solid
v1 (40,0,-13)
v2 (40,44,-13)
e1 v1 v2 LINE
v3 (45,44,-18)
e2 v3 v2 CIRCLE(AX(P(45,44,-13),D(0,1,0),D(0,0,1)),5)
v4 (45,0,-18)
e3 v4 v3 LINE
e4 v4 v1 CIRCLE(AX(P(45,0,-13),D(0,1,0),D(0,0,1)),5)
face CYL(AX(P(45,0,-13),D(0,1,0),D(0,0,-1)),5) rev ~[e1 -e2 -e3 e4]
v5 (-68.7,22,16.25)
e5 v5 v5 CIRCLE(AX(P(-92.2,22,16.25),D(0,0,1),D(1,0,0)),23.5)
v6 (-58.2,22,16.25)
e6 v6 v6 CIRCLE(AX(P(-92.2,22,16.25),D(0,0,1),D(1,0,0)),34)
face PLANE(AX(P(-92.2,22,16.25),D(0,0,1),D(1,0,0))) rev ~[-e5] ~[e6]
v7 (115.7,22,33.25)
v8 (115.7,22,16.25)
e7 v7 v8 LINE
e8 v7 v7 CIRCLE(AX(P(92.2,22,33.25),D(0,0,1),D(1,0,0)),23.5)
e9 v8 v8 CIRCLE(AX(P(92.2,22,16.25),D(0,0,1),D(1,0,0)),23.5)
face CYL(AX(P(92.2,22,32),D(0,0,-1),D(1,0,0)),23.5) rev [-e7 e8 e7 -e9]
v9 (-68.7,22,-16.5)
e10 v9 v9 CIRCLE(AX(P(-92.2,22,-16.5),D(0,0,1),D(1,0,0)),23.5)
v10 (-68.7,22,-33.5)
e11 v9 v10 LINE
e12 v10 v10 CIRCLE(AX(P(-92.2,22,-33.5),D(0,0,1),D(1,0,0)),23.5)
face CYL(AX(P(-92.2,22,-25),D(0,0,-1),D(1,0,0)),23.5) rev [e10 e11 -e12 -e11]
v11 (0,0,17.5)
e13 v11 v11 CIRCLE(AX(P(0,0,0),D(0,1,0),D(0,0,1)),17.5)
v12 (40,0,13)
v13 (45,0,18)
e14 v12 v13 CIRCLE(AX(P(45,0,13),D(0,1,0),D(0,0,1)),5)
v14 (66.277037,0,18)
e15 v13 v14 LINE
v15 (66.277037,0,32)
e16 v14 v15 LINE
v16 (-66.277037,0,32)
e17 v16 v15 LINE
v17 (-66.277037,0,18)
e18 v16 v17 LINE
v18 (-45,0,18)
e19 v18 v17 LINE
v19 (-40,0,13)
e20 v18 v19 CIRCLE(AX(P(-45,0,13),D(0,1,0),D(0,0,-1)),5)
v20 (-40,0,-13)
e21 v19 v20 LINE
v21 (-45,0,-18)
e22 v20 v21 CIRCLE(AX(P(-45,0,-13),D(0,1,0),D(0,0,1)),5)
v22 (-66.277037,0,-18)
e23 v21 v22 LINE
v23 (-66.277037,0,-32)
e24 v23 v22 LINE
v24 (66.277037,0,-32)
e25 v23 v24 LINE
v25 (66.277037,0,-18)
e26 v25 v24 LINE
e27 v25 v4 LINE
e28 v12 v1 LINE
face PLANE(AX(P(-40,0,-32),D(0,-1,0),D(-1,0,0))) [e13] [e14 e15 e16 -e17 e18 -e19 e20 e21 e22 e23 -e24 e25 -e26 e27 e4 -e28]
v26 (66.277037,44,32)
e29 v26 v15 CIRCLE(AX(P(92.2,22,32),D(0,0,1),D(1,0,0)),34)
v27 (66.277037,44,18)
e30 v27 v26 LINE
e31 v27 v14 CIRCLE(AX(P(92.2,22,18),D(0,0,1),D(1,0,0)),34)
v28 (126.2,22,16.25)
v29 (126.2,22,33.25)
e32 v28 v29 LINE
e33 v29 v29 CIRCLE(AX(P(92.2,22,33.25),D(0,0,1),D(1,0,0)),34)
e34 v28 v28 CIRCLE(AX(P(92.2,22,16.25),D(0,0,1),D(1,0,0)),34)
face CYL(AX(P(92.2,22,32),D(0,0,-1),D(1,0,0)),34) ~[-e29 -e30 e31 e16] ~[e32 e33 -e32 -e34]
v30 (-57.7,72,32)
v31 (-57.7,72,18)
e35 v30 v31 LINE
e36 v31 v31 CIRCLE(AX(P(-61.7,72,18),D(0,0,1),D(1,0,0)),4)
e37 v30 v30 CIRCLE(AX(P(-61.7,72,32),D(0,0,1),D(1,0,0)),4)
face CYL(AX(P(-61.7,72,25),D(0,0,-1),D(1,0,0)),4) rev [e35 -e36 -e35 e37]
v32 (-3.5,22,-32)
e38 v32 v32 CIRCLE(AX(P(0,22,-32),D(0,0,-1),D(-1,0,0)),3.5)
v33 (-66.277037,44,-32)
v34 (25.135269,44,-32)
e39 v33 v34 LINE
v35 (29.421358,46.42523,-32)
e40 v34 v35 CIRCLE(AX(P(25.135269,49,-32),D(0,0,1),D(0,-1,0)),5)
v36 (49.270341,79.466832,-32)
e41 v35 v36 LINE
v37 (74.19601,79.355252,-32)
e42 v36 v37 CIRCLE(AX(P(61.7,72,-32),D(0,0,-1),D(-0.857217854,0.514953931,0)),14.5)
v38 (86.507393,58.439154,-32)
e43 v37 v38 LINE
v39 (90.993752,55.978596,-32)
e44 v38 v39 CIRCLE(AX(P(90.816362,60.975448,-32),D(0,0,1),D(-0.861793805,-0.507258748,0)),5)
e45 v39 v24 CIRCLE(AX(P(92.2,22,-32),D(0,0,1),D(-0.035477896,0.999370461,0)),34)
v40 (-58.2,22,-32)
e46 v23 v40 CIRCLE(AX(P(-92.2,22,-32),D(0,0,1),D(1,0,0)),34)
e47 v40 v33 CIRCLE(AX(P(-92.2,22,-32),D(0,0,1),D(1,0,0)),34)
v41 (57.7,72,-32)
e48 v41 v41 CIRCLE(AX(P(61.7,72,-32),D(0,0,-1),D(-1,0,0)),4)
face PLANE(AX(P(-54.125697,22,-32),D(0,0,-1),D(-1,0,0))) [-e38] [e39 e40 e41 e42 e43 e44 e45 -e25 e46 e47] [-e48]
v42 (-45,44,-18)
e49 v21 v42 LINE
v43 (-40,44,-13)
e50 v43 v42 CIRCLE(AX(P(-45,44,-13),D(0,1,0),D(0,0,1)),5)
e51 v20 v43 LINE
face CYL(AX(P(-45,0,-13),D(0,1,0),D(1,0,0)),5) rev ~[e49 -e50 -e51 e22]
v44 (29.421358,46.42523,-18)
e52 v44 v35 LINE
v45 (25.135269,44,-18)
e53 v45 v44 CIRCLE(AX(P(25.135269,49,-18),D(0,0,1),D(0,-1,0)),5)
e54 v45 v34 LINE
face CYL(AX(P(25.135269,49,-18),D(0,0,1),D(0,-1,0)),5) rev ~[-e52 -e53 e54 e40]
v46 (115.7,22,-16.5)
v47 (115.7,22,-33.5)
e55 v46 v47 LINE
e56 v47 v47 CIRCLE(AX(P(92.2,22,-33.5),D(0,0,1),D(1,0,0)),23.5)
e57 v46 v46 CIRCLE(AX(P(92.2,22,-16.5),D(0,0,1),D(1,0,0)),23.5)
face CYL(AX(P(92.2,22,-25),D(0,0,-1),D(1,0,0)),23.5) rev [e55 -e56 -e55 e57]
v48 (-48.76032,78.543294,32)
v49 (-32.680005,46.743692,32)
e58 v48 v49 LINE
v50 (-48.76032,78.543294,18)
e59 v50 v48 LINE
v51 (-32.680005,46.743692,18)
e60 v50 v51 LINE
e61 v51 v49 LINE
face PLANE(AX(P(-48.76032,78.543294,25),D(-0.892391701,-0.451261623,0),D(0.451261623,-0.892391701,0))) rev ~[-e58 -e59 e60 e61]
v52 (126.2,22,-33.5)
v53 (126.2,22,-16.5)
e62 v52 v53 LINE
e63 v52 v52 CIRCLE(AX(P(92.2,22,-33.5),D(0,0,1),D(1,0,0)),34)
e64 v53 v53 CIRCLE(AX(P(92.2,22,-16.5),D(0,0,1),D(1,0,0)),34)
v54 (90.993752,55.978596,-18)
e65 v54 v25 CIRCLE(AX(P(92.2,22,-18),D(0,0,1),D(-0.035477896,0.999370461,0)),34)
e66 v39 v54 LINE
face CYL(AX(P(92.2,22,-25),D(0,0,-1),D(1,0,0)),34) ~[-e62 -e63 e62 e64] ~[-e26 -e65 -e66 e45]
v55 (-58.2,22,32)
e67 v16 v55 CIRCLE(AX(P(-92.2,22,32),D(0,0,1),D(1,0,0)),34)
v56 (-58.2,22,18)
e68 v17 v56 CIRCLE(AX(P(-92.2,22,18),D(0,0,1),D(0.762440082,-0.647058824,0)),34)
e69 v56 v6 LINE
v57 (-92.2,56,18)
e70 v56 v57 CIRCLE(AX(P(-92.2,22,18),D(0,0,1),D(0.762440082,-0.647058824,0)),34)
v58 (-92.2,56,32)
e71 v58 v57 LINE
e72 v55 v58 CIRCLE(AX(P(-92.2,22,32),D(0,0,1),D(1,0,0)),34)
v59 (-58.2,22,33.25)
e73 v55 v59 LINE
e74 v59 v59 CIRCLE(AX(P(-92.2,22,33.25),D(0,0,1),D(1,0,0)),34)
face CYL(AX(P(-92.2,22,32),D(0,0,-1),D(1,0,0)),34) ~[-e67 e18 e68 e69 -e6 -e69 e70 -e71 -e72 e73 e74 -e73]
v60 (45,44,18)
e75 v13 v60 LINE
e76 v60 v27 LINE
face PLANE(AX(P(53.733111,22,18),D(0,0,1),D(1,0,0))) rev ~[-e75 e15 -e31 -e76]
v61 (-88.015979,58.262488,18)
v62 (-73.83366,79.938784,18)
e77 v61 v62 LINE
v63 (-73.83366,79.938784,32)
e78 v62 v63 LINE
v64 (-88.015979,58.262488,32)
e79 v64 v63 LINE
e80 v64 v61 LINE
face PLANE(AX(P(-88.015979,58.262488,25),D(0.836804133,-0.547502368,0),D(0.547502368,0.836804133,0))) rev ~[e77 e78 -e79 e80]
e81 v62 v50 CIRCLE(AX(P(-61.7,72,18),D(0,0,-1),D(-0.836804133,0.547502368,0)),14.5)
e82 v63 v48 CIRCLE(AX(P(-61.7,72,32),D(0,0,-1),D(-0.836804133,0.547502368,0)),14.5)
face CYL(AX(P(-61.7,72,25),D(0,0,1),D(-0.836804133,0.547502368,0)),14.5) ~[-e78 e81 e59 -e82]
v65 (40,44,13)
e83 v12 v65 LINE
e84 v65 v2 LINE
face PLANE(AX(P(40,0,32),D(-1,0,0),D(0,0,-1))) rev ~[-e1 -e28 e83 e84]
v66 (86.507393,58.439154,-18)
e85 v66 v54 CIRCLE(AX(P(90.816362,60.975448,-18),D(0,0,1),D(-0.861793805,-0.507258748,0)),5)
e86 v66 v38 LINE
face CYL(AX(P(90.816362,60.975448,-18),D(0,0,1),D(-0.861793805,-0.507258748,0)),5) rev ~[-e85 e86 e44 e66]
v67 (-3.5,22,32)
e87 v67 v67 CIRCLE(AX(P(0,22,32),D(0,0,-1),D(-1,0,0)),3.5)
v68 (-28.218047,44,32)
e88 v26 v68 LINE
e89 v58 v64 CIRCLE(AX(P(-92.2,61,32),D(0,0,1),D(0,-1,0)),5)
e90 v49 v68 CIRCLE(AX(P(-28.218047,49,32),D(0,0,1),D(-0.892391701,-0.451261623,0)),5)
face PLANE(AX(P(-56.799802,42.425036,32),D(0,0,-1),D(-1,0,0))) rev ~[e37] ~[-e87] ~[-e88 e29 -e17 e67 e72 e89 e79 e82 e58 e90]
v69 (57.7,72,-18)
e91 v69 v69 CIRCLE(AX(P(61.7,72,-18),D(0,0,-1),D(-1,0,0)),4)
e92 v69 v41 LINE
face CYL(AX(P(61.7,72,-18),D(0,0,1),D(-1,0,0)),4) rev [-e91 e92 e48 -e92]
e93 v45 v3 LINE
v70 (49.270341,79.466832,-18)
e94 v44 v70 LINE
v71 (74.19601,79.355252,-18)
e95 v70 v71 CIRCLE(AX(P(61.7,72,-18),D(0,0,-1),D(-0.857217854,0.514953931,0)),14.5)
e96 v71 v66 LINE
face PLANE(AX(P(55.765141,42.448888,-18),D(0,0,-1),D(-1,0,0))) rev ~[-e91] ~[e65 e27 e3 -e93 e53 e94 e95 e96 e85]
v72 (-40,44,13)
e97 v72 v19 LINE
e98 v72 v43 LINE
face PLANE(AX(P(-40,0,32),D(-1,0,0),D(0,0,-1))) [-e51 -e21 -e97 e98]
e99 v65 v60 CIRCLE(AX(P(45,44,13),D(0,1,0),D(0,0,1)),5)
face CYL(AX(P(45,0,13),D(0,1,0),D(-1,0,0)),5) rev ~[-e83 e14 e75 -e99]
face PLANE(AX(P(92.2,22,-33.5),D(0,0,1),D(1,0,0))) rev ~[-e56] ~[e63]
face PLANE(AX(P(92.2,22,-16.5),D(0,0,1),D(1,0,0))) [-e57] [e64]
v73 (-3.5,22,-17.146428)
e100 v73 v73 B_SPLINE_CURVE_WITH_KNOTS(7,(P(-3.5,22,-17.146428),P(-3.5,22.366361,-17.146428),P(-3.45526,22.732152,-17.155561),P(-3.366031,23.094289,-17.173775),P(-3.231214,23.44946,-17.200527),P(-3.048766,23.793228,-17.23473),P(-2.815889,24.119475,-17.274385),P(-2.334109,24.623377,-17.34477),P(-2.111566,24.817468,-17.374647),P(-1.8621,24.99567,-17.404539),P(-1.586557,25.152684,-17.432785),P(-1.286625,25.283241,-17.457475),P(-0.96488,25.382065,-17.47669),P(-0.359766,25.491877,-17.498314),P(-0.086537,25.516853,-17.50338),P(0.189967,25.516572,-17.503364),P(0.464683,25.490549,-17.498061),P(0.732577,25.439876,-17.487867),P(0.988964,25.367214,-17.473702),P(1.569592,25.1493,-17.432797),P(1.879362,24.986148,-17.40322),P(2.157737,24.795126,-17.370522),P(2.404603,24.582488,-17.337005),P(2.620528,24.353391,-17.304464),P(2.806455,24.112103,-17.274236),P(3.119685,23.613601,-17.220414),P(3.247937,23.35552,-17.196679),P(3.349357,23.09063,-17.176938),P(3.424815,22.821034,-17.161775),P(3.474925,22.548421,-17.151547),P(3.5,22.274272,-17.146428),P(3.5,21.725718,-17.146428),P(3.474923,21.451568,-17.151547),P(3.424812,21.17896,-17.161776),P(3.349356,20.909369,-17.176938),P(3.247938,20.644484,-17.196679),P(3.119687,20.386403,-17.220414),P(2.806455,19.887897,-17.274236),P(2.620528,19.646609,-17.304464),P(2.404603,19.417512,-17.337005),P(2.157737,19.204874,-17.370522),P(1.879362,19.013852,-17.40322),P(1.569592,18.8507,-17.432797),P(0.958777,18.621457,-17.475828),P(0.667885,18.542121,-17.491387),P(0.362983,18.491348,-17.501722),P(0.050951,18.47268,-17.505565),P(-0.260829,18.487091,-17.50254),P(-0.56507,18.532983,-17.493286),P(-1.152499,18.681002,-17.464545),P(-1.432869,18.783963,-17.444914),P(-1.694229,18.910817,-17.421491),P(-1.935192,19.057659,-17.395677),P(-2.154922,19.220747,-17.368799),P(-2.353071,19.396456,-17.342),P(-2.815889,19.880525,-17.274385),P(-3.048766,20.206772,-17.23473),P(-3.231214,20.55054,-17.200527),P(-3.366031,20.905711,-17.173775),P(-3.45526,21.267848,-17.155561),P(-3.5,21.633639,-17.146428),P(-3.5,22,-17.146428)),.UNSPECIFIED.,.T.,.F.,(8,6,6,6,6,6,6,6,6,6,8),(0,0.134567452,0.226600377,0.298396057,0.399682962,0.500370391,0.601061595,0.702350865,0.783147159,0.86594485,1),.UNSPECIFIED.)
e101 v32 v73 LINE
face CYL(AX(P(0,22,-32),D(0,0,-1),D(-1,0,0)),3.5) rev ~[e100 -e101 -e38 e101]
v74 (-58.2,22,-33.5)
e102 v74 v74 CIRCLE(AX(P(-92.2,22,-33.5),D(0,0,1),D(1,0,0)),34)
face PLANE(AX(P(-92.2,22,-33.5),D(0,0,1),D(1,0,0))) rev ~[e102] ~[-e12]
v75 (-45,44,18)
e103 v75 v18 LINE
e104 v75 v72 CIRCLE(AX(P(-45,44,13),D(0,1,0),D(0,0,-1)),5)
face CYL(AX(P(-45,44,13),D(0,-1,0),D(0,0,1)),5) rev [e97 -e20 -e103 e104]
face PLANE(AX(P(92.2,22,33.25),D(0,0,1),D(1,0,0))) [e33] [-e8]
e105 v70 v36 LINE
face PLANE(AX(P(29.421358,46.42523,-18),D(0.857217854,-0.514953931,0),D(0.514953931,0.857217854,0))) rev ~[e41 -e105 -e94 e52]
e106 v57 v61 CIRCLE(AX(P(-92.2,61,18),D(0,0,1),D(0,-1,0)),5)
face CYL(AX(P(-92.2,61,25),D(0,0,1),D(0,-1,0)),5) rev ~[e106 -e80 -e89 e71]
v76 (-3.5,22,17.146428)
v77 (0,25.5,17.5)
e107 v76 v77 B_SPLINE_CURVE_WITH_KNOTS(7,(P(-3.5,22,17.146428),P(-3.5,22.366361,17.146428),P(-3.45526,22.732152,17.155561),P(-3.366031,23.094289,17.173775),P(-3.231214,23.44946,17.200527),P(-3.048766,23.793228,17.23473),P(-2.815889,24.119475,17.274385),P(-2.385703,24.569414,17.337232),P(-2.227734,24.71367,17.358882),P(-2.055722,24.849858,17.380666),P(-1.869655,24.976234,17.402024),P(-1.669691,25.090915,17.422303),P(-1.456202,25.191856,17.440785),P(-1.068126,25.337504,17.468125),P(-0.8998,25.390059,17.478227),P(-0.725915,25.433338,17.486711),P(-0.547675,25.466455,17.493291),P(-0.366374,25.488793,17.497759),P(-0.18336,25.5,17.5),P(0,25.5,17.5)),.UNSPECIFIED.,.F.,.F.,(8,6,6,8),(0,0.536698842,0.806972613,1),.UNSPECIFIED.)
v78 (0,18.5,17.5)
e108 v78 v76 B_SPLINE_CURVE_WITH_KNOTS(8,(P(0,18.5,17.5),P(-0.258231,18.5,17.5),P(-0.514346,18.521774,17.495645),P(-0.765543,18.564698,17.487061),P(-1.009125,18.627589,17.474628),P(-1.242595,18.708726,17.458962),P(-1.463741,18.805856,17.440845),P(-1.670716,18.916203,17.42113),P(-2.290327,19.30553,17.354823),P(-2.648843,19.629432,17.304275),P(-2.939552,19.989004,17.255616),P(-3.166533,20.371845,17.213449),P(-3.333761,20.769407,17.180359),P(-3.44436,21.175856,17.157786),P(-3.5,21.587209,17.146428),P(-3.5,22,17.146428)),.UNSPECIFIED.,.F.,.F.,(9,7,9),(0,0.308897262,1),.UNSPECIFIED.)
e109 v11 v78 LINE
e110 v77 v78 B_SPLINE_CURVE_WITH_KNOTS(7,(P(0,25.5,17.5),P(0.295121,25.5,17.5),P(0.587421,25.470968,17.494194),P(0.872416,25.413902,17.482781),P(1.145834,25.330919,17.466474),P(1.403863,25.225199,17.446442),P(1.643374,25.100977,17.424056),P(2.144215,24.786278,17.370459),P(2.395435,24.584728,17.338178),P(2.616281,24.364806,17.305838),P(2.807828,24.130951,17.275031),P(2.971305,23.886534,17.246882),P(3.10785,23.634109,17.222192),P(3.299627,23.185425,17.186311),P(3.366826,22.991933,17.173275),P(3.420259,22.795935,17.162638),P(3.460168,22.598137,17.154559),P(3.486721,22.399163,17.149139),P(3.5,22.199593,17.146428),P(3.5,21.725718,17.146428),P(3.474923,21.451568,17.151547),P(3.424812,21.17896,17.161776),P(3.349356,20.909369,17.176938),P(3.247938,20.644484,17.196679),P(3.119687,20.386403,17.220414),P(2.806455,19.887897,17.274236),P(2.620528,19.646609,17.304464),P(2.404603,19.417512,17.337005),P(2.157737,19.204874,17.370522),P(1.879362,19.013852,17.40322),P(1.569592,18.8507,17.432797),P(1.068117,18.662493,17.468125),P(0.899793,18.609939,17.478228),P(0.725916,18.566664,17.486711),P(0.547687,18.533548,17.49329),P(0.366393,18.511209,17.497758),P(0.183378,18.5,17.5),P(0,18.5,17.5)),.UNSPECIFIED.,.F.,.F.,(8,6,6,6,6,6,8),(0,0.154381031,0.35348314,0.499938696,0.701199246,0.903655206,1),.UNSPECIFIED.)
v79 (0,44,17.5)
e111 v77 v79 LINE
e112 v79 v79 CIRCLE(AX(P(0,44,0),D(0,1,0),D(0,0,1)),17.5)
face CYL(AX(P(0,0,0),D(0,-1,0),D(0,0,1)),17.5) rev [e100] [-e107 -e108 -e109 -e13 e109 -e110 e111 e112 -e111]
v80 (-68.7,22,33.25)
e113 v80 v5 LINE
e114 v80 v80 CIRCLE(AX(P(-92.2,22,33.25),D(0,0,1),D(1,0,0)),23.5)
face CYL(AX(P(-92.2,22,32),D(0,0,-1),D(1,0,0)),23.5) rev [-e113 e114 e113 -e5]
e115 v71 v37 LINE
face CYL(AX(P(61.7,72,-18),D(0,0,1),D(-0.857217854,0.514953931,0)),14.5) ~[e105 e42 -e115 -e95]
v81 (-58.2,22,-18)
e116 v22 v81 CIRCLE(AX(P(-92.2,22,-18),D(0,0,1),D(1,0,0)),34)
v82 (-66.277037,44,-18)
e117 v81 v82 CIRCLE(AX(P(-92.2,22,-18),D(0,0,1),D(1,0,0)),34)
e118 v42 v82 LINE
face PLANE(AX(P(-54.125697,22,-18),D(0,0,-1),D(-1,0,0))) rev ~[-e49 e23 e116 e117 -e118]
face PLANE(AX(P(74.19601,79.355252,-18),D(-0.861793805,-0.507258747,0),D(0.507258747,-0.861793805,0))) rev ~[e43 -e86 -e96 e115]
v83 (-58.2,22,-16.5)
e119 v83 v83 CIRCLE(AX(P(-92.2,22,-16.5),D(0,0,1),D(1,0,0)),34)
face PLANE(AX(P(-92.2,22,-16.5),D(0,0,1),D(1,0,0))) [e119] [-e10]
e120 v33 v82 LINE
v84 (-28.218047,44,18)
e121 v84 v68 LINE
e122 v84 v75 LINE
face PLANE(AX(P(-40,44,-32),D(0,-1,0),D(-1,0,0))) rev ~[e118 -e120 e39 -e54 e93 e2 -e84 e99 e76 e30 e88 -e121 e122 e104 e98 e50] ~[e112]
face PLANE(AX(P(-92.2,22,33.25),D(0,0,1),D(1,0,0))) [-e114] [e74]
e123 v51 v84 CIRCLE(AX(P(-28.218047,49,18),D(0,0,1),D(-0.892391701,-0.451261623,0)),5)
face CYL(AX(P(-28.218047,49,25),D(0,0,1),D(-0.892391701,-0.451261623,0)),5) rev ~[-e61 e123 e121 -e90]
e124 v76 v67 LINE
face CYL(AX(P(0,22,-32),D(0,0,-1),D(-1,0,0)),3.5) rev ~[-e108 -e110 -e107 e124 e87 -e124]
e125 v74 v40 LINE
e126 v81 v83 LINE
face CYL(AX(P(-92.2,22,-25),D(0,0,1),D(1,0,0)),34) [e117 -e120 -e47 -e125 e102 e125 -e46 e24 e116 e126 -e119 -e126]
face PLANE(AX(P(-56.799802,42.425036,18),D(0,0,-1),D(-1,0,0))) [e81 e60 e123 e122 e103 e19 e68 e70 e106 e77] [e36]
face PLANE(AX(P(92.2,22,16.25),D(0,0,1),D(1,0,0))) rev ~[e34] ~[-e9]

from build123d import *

# Parameters (mm, degrees)
CENTER_BODY_SKETCH_W         = 80
CENTER_BODY_SKETCH_H         = 64
CENTER_BODY_SKETCH_R         = 17.5
CENTER_BODY_DEPTH            = 44
PIVOT_EYES_SKETCH_R          = 34
PIVOT_EYES_SKETCH_R_2        = 23.5
PIVOT_EYES_68X_47_DEPTH      = 15.75
PIVOT_EYES_68X_47_2_DEPTH    = 15.75
EYE_FACE_PADS_SKETCH_R       = 34
EYE_FACE_PADS_SKETCH_R_2     = 23.5
EYE_FACE_PADS_DEPTH          = 1.25
MOUNTING_LUG_A_SKETCH_W      = 27.466221721
MOUNTING_LUG_A_SKETCH_H      = 44
MOUNTING_LUG_A_SKETCH_R      = 4
MOUNTING_LUG_A_DEPTH         = 7
MOUNTING_START               = -14
MOUNTING_LUG_B_SKETCH_R      = 4
MOUNTING_LUG_B_DEPTH         = 14
OFFSET_PIVOT_EYES_SKETCH_R   = 34
OFFSET_PIVOT_EYES_SKETCH_R_2 = 23.5
OFFSET_PIVOT_EYES_DEPTH      = 8.5
CENTER_WEB_SKETCH_W          = 28.251394121
CENTER_WEB_SKETCH_H          = 44
CENTER_WEB_DEPTH             = 14
PIN_HOLE_SKETCH_R            = 3.5
PIN_HOLE_7_DEPTH             = 200
LUG_A_FILLETS_R5_R           = 5
LUG_B_FILLETS_R5_R           = 5


with BuildPart() as part:
    # Center Body Sketch → Center Body (new body)
    with BuildSketch(Plane(origin=(0, 0, 0), x_dir=(1, 0, 0), z_dir=(0, 1, 0))):
        Rectangle(CENTER_BODY_SKETCH_W, CENTER_BODY_SKETCH_H)
        with Locations(Location((0, 0, 0), (0, 0, 270))):
            Circle(CENTER_BODY_SKETCH_R, mode=Mode.SUBTRACT)
    extrude(amount=CENTER_BODY_DEPTH)



with BuildPart() as body_2:
    # Pivot Eyes Sketch → Pivot Eyes Ø68xØ47 (new body)
    with BuildSketch(Plane.XY.offset(32)):
        with Locations((-92.2, 22)):
            Circle(PIVOT_EYES_SKETCH_R)
        with Locations((-92.2, 22)):
            Circle(PIVOT_EYES_SKETCH_R_2, mode=Mode.SUBTRACT)
    extrude(amount=-PIVOT_EYES_68X_47_DEPTH)



with BuildPart() as body_3:
    # Pivot Eyes Sketch → Pivot Eyes _68x_47 2 (new body)
    with BuildSketch(Plane.XY.offset(32)):
        with Locations((92.2, 22)):
            Circle(PIVOT_EYES_SKETCH_R)
        with Locations((92.2, 22)):
            Circle(PIVOT_EYES_SKETCH_R_2, mode=Mode.SUBTRACT)
    extrude(amount=-PIVOT_EYES_68X_47_2_DEPTH)


with BuildPart() as body_2_1:
    add(body_2.part)

    add(body_3.part)  # Eye Face Pads merges body 3
    # Eye Face Pads Sketch → Eye Face Pads (add)
    # profile 1 of 2: a face of its own
    with BuildSketch(Plane.XY.offset(32)):
        with Locations((-92.2, 22)):
            Circle(EYE_FACE_PADS_SKETCH_R)
        with Locations((-92.2, 22)):
            Circle(EYE_FACE_PADS_SKETCH_R_2, mode=Mode.SUBTRACT)
    # profile 2 of 2: a face of its own
    with BuildSketch(Plane.XY.offset(32)):
        with Locations((92.2, 22)):
            Circle(EYE_FACE_PADS_SKETCH_R)
        with Locations((92.2, 22)):
            Circle(EYE_FACE_PADS_SKETCH_R_2, mode=Mode.SUBTRACT)
    extrude(amount=EYE_FACE_PADS_DEPTH)


with BuildPart() as part_1:
    add(part.part)

    add(body_2_1.part)  # Mounting Lug A merges body 2
    # Mounting Lug A Sketch → Mounting Lug A (add, symmetric)
    # profile 1 of 2: a face of its own
    with BuildSketch(Plane.XY.offset(25)):
        with Locations((53.733110861, 22)):
            Rectangle(MOUNTING_LUG_A_SKETCH_W, MOUNTING_LUG_A_SKETCH_H)
    # profile 2 of 2: a face of its own
    with BuildSketch(Plane.XY.offset(25)):
        with BuildLine():
            Line((-40, 44), (-40, 0))
            Line((-40, 0), (-66.277037206, 0))
            ThreePointArc((-66.277037206, 0), (-61.345502759, 36.282856857), (-92.2, 56))
            ThreePointArc((-92.2, 56), (-89.821719025, 56.601843613), (-88.015979336, 58.262488159))
            Line((-88.015979336, 58.262488159), (-73.833659926, 79.93878434))
            ThreePointArc((-73.833659926, 79.93878434), (-60.894229811, 86.47759422), (-48.760320341, 78.543293537))
            Line((-48.760320341, 78.543293537), (-32.680005104, 46.743691884))
            ThreePointArc((-32.680005104, 46.743691884), (-30.837059719, 44.740801685), (-28.218046601, 44))
            Line((-28.218046601, 44), (-40, 44))
        make_face()
        with Locations((-61.7, 72)):
            Circle(MOUNTING_LUG_A_SKETCH_R, mode=Mode.SUBTRACT)
    extrude(amount=MOUNTING_LUG_A_DEPTH, both=True)

    # Mounting Lug B Sketch → Mounting Lug B (add)
    with BuildSketch(Plane(origin=(0, 0, -32), x_dir=(-1, 0, 0), z_dir=(0, 0, -1)).offset(MOUNTING_START)):
        with BuildLine():
            Line((-40, 44), (-25.135268802, 44))
            ThreePointArc((-25.135268802, 44), (-27.59760019, 44.648342369), (-29.421358071, 46.425230346))
            Line((-29.421358071, 46.425230346), (-49.270341118, 79.466831997))
            ThreePointArc((-49.270341118, 79.466831997), (-61.764908832, 86.499854718), (-74.196010179, 79.355251839))
            Line((-74.196010179, 79.355251839), (-86.507393015, 58.439154252))
            ThreePointArc((-86.507393015, 58.439154252), (-88.41197553, 56.591508495), (-90.993751524, 55.978595683))
            ThreePointArc((-90.993751524, 55.978595683), (-61.096956424, 35.733196289), (-66.277037206, 0))
            Line((-66.277037206, 0), (-40, 0))
            Line((-40, 0), (-40, 44))
        make_face()
        with Locations((-61.7, 72)):
            Circle(MOUNTING_LUG_B_SKETCH_R, mode=Mode.SUBTRACT)
    extrude(amount=MOUNTING_LUG_B_DEPTH)

    # Offset Pivot Eyes Sketch → Offset Pivot Eyes (add, symmetric)
    # profile 1 of 2: a face of its own
    with BuildSketch(Plane.XY.offset(-25)):
        with Locations((92.2, 22)):
            Circle(OFFSET_PIVOT_EYES_SKETCH_R)
        with Locations((92.2, 22)):
            Circle(OFFSET_PIVOT_EYES_SKETCH_R_2, mode=Mode.SUBTRACT)
    # profile 2 of 2: a face of its own
    with BuildSketch(Plane.XY.offset(-25)):
        with Locations((-92.2, 22)):
            Circle(OFFSET_PIVOT_EYES_SKETCH_R)
        with Locations((-92.2, 22)):
            Circle(OFFSET_PIVOT_EYES_SKETCH_R_2, mode=Mode.SUBTRACT)
    extrude(amount=OFFSET_PIVOT_EYES_DEPTH, both=True)


with BuildPart() as offset_pivot_eyes_piece_1:
    # of the separate pieces the step leaves, piece 1, a body of its own (offset_pivot_eyes_pieces)
    add(part_1.part.solids().sort_by_distance((126.2, 22, -33.5))[0])



with BuildPart() as offset_pivot_eyes_piece_2:
    # of the separate pieces the step leaves, piece 2, a body of its own (offset_pivot_eyes_pieces)
    add(part_1.part.solids().sort_by_distance((-58.2, 22, -33.5))[0])


with BuildPart() as offset_pivot_eyes_piece_1_1:
    add(offset_pivot_eyes_piece_1.part)

    add(offset_pivot_eyes_piece_2.part)  # Center Web merges Offset Pivot Eyes piece 2
    # Center Web Sketch → Center Web (add)
    with BuildSketch(Plane(origin=(0, 0, -32), x_dir=(-1, 0, 0), z_dir=(0, 0, -1))):
        with Locations((54.125697061, 22)):
            Rectangle(CENTER_WEB_SKETCH_W, CENTER_WEB_SKETCH_H)
    extrude(amount=-CENTER_WEB_DEPTH)

    # Pin Hole Sketch → Pin Hole Ø7 (cut)
    with BuildSketch(Plane(origin=(0, 0, -32), x_dir=(-1, 0, 0), z_dir=(0, 0, -1))):
        with Locations((0, 22)):
            Circle(PIN_HOLE_SKETCH_R)
    extrude(amount=-PIN_HOLE_7_DEPTH, mode=Mode.SUBTRACT)

    # Lug A Fillets R5
    lug_a_fillets_r5_edges = [offset_pivot_eyes_piece_1_1.edges().sort_by_distance(p)[0] for p in [
        (-40, 22, -18),
        (-40, 22, 18),
    ]]
    fillet(lug_a_fillets_r5_edges, radius=LUG_A_FILLETS_R5_R)

    # Lug B Fillets R5
    lug_b_fillets_r5_edges = [offset_pivot_eyes_piece_1_1.edges().sort_by_distance(p)[0] for p in [
        (40, 22, 18),
        (40, 22, -18),
    ]]
    fillet(lug_b_fillets_r5_edges, radius=LUG_B_FILLETS_R5_R)


solid = offset_pivot_eyes_piece_1_1.part
